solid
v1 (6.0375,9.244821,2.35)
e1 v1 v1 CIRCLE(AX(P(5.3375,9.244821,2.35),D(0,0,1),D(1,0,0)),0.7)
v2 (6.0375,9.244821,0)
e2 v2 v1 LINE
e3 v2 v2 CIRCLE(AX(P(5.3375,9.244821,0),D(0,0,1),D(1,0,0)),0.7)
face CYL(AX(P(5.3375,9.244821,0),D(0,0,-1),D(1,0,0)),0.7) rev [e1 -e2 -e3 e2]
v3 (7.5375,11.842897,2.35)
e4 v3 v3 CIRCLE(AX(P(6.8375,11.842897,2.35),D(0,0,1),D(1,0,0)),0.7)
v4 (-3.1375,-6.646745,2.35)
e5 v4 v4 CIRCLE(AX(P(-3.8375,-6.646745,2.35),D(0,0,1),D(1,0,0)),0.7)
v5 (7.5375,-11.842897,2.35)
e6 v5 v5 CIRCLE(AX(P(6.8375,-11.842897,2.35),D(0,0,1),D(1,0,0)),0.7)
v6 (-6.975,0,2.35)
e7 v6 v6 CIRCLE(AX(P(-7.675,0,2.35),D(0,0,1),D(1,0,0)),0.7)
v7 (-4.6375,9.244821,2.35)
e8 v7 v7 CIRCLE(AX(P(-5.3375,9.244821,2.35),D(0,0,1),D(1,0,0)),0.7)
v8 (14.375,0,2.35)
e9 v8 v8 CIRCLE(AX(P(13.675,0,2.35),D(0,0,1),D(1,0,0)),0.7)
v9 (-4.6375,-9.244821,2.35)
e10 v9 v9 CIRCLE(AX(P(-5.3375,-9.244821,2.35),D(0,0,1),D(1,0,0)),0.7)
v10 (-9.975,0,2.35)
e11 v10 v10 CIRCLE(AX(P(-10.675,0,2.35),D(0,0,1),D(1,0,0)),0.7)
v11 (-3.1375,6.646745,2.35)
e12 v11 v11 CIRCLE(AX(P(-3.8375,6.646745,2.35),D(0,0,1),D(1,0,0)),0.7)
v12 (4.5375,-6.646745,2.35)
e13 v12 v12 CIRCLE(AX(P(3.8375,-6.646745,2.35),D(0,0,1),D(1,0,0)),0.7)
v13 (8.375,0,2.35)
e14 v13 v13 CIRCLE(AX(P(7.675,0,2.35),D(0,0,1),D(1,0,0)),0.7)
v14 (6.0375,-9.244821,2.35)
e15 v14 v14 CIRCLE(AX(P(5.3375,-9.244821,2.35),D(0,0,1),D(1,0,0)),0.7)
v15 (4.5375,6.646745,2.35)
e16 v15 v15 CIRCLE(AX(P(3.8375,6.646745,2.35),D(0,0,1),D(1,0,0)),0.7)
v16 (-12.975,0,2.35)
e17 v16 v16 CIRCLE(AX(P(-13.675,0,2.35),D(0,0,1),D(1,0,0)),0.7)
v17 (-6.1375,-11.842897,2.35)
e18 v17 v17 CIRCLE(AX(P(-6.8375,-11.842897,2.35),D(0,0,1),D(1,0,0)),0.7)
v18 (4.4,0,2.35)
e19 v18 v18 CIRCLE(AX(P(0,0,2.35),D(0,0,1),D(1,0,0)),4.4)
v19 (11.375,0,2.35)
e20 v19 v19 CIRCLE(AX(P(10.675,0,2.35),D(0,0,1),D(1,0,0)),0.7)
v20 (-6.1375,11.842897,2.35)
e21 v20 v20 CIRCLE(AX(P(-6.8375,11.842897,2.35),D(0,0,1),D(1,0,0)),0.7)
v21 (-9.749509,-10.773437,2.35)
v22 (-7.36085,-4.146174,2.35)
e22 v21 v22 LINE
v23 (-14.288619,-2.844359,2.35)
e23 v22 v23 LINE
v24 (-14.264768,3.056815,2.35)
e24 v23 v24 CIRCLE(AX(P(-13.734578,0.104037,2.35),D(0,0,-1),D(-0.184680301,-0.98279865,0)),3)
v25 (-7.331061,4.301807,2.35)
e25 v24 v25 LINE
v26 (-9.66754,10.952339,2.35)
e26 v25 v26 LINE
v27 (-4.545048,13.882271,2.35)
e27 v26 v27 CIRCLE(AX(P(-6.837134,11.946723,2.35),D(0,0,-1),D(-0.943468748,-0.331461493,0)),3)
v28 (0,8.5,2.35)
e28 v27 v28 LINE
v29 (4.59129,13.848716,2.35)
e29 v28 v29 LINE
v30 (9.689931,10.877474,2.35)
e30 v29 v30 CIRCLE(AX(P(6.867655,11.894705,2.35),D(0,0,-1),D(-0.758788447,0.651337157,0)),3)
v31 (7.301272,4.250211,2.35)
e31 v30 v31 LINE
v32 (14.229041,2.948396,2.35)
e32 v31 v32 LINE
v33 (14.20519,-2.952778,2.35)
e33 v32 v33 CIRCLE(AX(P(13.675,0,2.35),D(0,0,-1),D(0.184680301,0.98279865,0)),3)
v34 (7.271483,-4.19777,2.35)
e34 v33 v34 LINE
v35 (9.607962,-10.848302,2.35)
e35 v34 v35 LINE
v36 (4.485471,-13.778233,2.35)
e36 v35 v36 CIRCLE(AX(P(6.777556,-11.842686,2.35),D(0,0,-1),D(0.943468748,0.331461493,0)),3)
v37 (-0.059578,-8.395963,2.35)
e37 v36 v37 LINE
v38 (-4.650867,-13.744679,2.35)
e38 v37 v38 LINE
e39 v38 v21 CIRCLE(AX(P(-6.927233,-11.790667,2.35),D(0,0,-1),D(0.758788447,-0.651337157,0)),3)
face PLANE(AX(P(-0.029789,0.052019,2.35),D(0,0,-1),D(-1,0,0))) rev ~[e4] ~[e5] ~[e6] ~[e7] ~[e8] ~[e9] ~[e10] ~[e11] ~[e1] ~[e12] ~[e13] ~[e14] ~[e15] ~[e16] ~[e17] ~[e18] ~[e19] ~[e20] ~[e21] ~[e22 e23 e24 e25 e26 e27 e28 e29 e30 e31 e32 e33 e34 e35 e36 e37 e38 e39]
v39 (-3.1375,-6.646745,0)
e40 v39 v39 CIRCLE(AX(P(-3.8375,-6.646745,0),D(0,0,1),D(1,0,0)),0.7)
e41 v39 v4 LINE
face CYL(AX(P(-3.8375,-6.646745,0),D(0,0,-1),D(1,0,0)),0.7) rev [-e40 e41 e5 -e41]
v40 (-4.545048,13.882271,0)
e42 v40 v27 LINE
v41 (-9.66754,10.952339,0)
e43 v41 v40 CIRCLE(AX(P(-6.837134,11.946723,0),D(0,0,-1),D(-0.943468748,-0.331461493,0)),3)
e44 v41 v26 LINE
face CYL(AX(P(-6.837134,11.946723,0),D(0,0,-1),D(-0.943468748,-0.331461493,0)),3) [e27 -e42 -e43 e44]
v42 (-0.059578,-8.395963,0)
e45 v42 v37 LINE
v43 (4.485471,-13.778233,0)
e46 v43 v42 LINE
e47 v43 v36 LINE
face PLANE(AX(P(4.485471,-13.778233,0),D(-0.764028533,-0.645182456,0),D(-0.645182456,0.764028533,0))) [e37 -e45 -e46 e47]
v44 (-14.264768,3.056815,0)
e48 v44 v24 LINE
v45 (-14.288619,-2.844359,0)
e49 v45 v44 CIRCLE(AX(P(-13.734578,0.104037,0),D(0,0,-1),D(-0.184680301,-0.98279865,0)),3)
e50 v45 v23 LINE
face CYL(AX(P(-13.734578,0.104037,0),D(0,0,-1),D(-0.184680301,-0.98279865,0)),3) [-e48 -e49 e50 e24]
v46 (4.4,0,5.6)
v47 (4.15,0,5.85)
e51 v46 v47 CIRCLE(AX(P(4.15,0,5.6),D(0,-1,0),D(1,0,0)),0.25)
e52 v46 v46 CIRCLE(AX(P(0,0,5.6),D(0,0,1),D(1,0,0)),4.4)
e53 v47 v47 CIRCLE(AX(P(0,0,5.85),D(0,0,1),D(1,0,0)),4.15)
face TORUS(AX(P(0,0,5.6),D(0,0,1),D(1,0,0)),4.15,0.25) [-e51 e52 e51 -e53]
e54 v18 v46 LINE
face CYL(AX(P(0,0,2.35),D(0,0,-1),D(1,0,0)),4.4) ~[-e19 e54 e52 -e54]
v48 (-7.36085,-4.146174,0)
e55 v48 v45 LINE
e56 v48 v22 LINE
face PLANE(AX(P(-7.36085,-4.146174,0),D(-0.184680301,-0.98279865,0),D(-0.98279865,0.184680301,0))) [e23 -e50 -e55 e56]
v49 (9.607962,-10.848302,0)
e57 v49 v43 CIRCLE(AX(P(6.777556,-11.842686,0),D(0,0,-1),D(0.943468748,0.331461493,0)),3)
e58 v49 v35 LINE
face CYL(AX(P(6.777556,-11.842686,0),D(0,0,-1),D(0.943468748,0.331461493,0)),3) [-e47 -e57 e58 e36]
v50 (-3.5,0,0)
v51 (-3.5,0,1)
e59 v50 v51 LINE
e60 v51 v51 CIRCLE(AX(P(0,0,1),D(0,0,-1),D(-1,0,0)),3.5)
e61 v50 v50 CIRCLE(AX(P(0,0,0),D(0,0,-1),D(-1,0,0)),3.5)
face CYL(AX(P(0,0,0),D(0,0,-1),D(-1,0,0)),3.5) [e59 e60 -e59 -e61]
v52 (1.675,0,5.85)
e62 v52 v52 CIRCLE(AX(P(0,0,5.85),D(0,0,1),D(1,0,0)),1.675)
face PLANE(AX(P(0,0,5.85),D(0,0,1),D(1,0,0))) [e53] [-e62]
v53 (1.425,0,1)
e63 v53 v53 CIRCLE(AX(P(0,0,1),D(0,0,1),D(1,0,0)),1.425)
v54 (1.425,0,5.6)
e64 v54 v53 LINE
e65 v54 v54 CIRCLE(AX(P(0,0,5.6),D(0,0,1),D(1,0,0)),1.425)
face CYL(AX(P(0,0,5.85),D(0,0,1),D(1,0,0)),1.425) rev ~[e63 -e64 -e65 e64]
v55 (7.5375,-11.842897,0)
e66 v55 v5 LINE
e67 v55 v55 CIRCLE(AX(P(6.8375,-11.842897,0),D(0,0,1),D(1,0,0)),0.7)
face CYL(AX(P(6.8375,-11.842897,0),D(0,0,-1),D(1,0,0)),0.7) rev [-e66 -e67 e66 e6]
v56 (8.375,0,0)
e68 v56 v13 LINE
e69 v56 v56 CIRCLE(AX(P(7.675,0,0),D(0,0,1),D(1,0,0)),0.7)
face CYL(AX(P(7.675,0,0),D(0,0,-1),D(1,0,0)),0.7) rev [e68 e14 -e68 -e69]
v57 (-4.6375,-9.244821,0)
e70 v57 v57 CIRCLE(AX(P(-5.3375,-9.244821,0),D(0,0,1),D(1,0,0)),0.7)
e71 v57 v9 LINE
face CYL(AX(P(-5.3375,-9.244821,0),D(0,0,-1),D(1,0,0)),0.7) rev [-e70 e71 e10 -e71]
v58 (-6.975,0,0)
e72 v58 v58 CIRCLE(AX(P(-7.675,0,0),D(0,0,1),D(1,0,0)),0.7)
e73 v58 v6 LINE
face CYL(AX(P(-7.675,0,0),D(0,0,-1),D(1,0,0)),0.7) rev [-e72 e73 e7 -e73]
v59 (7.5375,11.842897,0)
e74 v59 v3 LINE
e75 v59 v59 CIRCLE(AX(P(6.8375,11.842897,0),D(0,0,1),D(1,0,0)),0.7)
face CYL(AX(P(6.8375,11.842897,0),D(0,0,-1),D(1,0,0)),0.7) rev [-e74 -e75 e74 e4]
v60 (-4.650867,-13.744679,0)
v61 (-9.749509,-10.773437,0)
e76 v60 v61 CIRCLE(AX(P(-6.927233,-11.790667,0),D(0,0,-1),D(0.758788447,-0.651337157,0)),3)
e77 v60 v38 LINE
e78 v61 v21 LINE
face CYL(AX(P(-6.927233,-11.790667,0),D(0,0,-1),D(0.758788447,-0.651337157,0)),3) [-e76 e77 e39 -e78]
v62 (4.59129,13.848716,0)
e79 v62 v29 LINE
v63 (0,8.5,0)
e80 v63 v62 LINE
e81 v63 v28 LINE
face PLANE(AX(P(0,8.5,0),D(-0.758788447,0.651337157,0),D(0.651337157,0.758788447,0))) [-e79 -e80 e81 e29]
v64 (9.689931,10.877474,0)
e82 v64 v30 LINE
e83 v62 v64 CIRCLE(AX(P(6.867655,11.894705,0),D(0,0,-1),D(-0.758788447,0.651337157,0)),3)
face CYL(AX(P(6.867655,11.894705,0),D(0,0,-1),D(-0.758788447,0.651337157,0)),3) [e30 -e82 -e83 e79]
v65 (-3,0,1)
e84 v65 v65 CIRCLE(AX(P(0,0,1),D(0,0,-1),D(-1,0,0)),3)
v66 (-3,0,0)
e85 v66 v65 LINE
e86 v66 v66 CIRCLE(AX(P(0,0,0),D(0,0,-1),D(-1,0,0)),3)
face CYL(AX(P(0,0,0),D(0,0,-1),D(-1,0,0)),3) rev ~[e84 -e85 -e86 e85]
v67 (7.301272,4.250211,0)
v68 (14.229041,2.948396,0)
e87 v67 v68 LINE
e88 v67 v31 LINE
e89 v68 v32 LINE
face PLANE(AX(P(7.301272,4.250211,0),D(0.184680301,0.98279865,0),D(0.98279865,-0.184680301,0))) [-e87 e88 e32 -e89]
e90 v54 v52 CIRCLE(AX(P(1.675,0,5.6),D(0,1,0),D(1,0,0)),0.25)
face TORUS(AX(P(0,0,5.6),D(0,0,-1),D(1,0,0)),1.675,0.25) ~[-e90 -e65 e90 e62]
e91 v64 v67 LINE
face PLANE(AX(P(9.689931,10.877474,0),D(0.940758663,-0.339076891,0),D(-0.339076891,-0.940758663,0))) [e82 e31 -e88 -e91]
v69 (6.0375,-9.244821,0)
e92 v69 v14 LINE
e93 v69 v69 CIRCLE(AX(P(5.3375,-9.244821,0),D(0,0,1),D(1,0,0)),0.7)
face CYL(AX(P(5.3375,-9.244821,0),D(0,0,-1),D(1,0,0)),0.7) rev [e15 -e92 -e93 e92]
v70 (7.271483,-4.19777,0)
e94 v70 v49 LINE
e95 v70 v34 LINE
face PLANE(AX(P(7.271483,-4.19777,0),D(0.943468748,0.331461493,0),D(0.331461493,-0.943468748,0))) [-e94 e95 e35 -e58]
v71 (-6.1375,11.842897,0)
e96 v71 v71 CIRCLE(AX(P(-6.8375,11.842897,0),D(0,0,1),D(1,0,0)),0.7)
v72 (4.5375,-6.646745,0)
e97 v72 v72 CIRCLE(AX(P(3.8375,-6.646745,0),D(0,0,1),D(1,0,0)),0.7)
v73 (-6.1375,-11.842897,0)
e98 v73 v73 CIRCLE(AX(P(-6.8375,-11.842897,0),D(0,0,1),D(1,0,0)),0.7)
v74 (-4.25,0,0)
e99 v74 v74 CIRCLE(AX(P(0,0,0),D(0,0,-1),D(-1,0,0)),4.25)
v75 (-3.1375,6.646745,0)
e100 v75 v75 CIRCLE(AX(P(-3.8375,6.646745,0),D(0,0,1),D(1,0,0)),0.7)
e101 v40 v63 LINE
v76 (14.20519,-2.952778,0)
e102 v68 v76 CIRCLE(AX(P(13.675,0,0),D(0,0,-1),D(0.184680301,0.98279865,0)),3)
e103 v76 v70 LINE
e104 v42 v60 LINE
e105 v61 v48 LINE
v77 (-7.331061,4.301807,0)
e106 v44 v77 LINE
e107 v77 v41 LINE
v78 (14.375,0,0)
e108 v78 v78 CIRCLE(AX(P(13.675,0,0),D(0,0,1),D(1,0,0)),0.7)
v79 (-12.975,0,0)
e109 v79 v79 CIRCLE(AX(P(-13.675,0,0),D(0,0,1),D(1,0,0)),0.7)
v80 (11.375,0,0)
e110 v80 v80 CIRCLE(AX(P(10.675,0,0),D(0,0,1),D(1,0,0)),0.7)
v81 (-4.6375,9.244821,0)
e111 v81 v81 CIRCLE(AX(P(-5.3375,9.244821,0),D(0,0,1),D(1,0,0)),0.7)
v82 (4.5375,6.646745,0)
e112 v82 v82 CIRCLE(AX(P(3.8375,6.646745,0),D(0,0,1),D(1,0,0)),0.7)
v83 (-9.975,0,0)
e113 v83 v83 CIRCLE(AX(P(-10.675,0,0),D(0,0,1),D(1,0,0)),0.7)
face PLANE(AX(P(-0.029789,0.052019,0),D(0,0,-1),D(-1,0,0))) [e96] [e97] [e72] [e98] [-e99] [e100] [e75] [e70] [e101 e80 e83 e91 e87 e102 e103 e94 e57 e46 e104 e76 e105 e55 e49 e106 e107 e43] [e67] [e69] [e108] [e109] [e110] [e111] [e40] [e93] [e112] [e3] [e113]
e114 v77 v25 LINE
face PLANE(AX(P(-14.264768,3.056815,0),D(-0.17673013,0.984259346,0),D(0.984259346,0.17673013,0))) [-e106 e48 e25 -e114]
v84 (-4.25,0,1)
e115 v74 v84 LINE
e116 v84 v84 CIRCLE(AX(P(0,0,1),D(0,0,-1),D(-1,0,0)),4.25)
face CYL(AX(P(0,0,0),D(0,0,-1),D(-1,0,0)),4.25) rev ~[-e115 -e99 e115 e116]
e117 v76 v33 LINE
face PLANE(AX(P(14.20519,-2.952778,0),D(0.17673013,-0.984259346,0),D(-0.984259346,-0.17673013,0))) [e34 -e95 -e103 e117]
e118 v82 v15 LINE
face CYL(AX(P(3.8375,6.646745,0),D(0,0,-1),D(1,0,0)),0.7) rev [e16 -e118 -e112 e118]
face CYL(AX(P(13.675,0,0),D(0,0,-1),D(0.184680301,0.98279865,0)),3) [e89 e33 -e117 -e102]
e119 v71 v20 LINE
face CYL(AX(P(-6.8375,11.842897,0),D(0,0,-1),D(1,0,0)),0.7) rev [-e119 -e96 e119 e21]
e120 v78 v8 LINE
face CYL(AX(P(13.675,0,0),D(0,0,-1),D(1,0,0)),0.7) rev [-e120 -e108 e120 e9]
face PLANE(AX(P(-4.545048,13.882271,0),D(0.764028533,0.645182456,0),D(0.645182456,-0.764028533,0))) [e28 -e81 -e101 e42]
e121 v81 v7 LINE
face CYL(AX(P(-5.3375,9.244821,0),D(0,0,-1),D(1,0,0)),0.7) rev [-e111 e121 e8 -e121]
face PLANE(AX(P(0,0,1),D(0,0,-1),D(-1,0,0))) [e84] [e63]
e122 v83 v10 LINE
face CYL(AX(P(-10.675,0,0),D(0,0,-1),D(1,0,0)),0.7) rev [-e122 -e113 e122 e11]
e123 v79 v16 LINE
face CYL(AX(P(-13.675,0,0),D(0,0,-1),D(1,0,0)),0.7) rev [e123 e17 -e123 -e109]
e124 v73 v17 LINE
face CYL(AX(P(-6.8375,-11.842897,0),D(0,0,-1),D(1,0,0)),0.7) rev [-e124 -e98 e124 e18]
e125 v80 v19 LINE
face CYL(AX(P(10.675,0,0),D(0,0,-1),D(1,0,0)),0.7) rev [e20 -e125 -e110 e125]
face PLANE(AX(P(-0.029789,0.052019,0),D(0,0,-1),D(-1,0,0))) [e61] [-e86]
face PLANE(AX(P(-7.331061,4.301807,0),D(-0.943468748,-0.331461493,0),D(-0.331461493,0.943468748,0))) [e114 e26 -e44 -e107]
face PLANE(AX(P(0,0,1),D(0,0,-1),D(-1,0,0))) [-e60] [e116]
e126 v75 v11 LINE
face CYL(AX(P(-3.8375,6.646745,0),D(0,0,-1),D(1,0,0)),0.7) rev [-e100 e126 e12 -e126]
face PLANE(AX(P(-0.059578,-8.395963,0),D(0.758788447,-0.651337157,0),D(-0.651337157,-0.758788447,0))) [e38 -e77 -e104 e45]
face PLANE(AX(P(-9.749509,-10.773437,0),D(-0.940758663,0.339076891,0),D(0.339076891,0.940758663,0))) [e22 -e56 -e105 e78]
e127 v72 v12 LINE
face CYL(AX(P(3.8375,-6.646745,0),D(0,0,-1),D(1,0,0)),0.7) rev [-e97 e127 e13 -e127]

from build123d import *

# Parameters (mm, degrees)
SKETCH_1_R          = 0.7
EXTRUDE_1_DEPTH     = 2.35
SKETCH_2_R          = 4.4
EXTRUDE_2_DEPTH     = 3.5
SKETCH_3_R          = 1.425
CUT_EXTRUDE_1_DEPTH = 24.187779754
FILLET_1_R          = 0.25
SKETCH_4_R          = 4.25
SKETCH_4_R_2        = 3.5
CUT_EXTRUDE_2_DEPTH = 1
SKETCH_5_R          = 3
CUT_EXTRUDE_3_DEPTH = 1


with BuildPart() as part:
    # 草图1 → 凸台-拉伸1 (new body)
    with BuildSketch(Plane.XY):
        with BuildLine():
            Line((-4.545048295, 13.882270629), (0, 8.5))
            Line((0, 8.5), (4.591289657, 13.848716116))
            ThreePointArc((4.591289657, 13.848716116), (8.378143191, 14.486697202), (9.689930988, 10.877473971))
            Line((9.689930988, 10.877473971), (7.301272041, 4.250211371))
            Line((7.301272041, 4.250211371), (14.229040903, 2.94839595))
            ThreePointArc((14.229040903, 2.94839595), (16.674975498, -0.012124868), (14.20519039, -2.952778039))
            Line((14.20519039, -2.952778039), (7.271483148, -4.19777001))
            Line((7.271483148, -4.19777001), (9.607962353, -10.848301547))
            ThreePointArc((9.607962353, -10.848301547), (8.267043414, -14.446803451), (4.48547051, -13.778233392))
            Line((4.48547051, -13.778233392), (-0.059577785, -8.395962763))
            Line((-0.059577785, -8.395962763), (-4.650867443, -13.744678878))
            ThreePointArc((-4.650867443, -13.744678878), (-8.437720976, -14.382659965), (-9.749508773, -10.773436734))
            Line((-9.749508773, -10.773436734), (-7.360849826, -4.146174134))
            Line((-7.360849826, -4.146174134), (-14.288618688, -2.844358713))
            ThreePointArc((-14.288618688, -2.844358713), (-16.734553283, 0.116162105), (-14.264768176, 3.056815277))
            Line((-14.264768176, 3.056815277), (-7.331060933, 4.301807247))
            Line((-7.331060933, 4.301807247), (-9.667540138, 10.952338784))
            ThreePointArc((-9.667540138, 10.952338784), (-8.326621199, 14.550840688), (-4.545048295, 13.882270629))
        make_face()
        with Locations((13.675, 0)):
            Circle(SKETCH_1_R, mode=Mode.SUBTRACT)
        with Locations((10.675, 0)):
            Circle(SKETCH_1_R, mode=Mode.SUBTRACT)
        with Locations((7.675, 0)):
            Circle(SKETCH_1_R, mode=Mode.SUBTRACT)
        with Locations((3.8375, -6.646744974)):
            Circle(SKETCH_1_R, mode=Mode.SUBTRACT)
        with Locations((5.3375, -9.244821185)):
            Circle(SKETCH_1_R, mode=Mode.SUBTRACT)
        with Locations((6.8375, -11.842897397)):
            Circle(SKETCH_1_R, mode=Mode.SUBTRACT)
        with Locations((-3.8375, -6.646744974)):
            Circle(SKETCH_1_R, mode=Mode.SUBTRACT)
        with Locations((-5.3375, -9.244821185)):
            Circle(SKETCH_1_R, mode=Mode.SUBTRACT)
        with Locations((-6.8375, -11.842897397)):
            Circle(SKETCH_1_R, mode=Mode.SUBTRACT)
        with Locations((-7.675, 0)):
            Circle(SKETCH_1_R, mode=Mode.SUBTRACT)
        with Locations((-10.675, 0)):
            Circle(SKETCH_1_R, mode=Mode.SUBTRACT)
        with Locations((-13.675, 0)):
            Circle(SKETCH_1_R, mode=Mode.SUBTRACT)
        with Locations((-3.8375, 6.646744974)):
            Circle(SKETCH_1_R, mode=Mode.SUBTRACT)
        with Locations((-5.3375, 9.244821185)):
            Circle(SKETCH_1_R, mode=Mode.SUBTRACT)
        with Locations((-6.8375, 11.842897397)):
            Circle(SKETCH_1_R, mode=Mode.SUBTRACT)
        with Locations((3.8375, 6.646744974)):
            Circle(SKETCH_1_R, mode=Mode.SUBTRACT)
        with Locations((5.3375, 9.244821185)):
            Circle(SKETCH_1_R, mode=Mode.SUBTRACT)
        with Locations((6.8375, 11.842897397)):
            Circle(SKETCH_1_R, mode=Mode.SUBTRACT)
    extrude(amount=EXTRUDE_1_DEPTH)

    # 草图2 → 凸台-拉伸2 (add)
    with BuildSketch(Plane.XY.offset(2.35)):
        Circle(SKETCH_2_R)
    extrude(amount=EXTRUDE_2_DEPTH)

    # 草图3 → 切除-拉伸1 (cut, through all)
    with BuildSketch(Plane.XY.offset(5.85)):
        Circle(SKETCH_3_R)
    extrude(amount=-CUT_EXTRUDE_1_DEPTH, mode=Mode.SUBTRACT)

    # 圆角1
    fillet_1_edges = [part.edges().sort_by_distance(p)[0] for p in [
        (-4.4, 0, 5.85),
        (-1.425, 0, 5.85),
    ]]
    fillet(fillet_1_edges, radius=FILLET_1_R)

    # 草图4 → 切除-拉伸2 (cut)
    with BuildSketch(Plane(origin=(0, 0, 0), x_dir=(-1, 0, 0), z_dir=(0, 0, -1))):
        Circle(SKETCH_4_R)
        Circle(SKETCH_4_R_2, mode=Mode.SUBTRACT)
    extrude(amount=-CUT_EXTRUDE_2_DEPTH, mode=Mode.SUBTRACT)

    # 草图5 → 切除-拉伸3 (cut)
    with BuildSketch(Plane(origin=(0, 0, 0), x_dir=(-1, 0, 0), z_dir=(0, 0, -1))):
        Circle(SKETCH_5_R)
    extrude(amount=-CUT_EXTRUDE_3_DEPTH, mode=Mode.SUBTRACT)


solid = part.part
